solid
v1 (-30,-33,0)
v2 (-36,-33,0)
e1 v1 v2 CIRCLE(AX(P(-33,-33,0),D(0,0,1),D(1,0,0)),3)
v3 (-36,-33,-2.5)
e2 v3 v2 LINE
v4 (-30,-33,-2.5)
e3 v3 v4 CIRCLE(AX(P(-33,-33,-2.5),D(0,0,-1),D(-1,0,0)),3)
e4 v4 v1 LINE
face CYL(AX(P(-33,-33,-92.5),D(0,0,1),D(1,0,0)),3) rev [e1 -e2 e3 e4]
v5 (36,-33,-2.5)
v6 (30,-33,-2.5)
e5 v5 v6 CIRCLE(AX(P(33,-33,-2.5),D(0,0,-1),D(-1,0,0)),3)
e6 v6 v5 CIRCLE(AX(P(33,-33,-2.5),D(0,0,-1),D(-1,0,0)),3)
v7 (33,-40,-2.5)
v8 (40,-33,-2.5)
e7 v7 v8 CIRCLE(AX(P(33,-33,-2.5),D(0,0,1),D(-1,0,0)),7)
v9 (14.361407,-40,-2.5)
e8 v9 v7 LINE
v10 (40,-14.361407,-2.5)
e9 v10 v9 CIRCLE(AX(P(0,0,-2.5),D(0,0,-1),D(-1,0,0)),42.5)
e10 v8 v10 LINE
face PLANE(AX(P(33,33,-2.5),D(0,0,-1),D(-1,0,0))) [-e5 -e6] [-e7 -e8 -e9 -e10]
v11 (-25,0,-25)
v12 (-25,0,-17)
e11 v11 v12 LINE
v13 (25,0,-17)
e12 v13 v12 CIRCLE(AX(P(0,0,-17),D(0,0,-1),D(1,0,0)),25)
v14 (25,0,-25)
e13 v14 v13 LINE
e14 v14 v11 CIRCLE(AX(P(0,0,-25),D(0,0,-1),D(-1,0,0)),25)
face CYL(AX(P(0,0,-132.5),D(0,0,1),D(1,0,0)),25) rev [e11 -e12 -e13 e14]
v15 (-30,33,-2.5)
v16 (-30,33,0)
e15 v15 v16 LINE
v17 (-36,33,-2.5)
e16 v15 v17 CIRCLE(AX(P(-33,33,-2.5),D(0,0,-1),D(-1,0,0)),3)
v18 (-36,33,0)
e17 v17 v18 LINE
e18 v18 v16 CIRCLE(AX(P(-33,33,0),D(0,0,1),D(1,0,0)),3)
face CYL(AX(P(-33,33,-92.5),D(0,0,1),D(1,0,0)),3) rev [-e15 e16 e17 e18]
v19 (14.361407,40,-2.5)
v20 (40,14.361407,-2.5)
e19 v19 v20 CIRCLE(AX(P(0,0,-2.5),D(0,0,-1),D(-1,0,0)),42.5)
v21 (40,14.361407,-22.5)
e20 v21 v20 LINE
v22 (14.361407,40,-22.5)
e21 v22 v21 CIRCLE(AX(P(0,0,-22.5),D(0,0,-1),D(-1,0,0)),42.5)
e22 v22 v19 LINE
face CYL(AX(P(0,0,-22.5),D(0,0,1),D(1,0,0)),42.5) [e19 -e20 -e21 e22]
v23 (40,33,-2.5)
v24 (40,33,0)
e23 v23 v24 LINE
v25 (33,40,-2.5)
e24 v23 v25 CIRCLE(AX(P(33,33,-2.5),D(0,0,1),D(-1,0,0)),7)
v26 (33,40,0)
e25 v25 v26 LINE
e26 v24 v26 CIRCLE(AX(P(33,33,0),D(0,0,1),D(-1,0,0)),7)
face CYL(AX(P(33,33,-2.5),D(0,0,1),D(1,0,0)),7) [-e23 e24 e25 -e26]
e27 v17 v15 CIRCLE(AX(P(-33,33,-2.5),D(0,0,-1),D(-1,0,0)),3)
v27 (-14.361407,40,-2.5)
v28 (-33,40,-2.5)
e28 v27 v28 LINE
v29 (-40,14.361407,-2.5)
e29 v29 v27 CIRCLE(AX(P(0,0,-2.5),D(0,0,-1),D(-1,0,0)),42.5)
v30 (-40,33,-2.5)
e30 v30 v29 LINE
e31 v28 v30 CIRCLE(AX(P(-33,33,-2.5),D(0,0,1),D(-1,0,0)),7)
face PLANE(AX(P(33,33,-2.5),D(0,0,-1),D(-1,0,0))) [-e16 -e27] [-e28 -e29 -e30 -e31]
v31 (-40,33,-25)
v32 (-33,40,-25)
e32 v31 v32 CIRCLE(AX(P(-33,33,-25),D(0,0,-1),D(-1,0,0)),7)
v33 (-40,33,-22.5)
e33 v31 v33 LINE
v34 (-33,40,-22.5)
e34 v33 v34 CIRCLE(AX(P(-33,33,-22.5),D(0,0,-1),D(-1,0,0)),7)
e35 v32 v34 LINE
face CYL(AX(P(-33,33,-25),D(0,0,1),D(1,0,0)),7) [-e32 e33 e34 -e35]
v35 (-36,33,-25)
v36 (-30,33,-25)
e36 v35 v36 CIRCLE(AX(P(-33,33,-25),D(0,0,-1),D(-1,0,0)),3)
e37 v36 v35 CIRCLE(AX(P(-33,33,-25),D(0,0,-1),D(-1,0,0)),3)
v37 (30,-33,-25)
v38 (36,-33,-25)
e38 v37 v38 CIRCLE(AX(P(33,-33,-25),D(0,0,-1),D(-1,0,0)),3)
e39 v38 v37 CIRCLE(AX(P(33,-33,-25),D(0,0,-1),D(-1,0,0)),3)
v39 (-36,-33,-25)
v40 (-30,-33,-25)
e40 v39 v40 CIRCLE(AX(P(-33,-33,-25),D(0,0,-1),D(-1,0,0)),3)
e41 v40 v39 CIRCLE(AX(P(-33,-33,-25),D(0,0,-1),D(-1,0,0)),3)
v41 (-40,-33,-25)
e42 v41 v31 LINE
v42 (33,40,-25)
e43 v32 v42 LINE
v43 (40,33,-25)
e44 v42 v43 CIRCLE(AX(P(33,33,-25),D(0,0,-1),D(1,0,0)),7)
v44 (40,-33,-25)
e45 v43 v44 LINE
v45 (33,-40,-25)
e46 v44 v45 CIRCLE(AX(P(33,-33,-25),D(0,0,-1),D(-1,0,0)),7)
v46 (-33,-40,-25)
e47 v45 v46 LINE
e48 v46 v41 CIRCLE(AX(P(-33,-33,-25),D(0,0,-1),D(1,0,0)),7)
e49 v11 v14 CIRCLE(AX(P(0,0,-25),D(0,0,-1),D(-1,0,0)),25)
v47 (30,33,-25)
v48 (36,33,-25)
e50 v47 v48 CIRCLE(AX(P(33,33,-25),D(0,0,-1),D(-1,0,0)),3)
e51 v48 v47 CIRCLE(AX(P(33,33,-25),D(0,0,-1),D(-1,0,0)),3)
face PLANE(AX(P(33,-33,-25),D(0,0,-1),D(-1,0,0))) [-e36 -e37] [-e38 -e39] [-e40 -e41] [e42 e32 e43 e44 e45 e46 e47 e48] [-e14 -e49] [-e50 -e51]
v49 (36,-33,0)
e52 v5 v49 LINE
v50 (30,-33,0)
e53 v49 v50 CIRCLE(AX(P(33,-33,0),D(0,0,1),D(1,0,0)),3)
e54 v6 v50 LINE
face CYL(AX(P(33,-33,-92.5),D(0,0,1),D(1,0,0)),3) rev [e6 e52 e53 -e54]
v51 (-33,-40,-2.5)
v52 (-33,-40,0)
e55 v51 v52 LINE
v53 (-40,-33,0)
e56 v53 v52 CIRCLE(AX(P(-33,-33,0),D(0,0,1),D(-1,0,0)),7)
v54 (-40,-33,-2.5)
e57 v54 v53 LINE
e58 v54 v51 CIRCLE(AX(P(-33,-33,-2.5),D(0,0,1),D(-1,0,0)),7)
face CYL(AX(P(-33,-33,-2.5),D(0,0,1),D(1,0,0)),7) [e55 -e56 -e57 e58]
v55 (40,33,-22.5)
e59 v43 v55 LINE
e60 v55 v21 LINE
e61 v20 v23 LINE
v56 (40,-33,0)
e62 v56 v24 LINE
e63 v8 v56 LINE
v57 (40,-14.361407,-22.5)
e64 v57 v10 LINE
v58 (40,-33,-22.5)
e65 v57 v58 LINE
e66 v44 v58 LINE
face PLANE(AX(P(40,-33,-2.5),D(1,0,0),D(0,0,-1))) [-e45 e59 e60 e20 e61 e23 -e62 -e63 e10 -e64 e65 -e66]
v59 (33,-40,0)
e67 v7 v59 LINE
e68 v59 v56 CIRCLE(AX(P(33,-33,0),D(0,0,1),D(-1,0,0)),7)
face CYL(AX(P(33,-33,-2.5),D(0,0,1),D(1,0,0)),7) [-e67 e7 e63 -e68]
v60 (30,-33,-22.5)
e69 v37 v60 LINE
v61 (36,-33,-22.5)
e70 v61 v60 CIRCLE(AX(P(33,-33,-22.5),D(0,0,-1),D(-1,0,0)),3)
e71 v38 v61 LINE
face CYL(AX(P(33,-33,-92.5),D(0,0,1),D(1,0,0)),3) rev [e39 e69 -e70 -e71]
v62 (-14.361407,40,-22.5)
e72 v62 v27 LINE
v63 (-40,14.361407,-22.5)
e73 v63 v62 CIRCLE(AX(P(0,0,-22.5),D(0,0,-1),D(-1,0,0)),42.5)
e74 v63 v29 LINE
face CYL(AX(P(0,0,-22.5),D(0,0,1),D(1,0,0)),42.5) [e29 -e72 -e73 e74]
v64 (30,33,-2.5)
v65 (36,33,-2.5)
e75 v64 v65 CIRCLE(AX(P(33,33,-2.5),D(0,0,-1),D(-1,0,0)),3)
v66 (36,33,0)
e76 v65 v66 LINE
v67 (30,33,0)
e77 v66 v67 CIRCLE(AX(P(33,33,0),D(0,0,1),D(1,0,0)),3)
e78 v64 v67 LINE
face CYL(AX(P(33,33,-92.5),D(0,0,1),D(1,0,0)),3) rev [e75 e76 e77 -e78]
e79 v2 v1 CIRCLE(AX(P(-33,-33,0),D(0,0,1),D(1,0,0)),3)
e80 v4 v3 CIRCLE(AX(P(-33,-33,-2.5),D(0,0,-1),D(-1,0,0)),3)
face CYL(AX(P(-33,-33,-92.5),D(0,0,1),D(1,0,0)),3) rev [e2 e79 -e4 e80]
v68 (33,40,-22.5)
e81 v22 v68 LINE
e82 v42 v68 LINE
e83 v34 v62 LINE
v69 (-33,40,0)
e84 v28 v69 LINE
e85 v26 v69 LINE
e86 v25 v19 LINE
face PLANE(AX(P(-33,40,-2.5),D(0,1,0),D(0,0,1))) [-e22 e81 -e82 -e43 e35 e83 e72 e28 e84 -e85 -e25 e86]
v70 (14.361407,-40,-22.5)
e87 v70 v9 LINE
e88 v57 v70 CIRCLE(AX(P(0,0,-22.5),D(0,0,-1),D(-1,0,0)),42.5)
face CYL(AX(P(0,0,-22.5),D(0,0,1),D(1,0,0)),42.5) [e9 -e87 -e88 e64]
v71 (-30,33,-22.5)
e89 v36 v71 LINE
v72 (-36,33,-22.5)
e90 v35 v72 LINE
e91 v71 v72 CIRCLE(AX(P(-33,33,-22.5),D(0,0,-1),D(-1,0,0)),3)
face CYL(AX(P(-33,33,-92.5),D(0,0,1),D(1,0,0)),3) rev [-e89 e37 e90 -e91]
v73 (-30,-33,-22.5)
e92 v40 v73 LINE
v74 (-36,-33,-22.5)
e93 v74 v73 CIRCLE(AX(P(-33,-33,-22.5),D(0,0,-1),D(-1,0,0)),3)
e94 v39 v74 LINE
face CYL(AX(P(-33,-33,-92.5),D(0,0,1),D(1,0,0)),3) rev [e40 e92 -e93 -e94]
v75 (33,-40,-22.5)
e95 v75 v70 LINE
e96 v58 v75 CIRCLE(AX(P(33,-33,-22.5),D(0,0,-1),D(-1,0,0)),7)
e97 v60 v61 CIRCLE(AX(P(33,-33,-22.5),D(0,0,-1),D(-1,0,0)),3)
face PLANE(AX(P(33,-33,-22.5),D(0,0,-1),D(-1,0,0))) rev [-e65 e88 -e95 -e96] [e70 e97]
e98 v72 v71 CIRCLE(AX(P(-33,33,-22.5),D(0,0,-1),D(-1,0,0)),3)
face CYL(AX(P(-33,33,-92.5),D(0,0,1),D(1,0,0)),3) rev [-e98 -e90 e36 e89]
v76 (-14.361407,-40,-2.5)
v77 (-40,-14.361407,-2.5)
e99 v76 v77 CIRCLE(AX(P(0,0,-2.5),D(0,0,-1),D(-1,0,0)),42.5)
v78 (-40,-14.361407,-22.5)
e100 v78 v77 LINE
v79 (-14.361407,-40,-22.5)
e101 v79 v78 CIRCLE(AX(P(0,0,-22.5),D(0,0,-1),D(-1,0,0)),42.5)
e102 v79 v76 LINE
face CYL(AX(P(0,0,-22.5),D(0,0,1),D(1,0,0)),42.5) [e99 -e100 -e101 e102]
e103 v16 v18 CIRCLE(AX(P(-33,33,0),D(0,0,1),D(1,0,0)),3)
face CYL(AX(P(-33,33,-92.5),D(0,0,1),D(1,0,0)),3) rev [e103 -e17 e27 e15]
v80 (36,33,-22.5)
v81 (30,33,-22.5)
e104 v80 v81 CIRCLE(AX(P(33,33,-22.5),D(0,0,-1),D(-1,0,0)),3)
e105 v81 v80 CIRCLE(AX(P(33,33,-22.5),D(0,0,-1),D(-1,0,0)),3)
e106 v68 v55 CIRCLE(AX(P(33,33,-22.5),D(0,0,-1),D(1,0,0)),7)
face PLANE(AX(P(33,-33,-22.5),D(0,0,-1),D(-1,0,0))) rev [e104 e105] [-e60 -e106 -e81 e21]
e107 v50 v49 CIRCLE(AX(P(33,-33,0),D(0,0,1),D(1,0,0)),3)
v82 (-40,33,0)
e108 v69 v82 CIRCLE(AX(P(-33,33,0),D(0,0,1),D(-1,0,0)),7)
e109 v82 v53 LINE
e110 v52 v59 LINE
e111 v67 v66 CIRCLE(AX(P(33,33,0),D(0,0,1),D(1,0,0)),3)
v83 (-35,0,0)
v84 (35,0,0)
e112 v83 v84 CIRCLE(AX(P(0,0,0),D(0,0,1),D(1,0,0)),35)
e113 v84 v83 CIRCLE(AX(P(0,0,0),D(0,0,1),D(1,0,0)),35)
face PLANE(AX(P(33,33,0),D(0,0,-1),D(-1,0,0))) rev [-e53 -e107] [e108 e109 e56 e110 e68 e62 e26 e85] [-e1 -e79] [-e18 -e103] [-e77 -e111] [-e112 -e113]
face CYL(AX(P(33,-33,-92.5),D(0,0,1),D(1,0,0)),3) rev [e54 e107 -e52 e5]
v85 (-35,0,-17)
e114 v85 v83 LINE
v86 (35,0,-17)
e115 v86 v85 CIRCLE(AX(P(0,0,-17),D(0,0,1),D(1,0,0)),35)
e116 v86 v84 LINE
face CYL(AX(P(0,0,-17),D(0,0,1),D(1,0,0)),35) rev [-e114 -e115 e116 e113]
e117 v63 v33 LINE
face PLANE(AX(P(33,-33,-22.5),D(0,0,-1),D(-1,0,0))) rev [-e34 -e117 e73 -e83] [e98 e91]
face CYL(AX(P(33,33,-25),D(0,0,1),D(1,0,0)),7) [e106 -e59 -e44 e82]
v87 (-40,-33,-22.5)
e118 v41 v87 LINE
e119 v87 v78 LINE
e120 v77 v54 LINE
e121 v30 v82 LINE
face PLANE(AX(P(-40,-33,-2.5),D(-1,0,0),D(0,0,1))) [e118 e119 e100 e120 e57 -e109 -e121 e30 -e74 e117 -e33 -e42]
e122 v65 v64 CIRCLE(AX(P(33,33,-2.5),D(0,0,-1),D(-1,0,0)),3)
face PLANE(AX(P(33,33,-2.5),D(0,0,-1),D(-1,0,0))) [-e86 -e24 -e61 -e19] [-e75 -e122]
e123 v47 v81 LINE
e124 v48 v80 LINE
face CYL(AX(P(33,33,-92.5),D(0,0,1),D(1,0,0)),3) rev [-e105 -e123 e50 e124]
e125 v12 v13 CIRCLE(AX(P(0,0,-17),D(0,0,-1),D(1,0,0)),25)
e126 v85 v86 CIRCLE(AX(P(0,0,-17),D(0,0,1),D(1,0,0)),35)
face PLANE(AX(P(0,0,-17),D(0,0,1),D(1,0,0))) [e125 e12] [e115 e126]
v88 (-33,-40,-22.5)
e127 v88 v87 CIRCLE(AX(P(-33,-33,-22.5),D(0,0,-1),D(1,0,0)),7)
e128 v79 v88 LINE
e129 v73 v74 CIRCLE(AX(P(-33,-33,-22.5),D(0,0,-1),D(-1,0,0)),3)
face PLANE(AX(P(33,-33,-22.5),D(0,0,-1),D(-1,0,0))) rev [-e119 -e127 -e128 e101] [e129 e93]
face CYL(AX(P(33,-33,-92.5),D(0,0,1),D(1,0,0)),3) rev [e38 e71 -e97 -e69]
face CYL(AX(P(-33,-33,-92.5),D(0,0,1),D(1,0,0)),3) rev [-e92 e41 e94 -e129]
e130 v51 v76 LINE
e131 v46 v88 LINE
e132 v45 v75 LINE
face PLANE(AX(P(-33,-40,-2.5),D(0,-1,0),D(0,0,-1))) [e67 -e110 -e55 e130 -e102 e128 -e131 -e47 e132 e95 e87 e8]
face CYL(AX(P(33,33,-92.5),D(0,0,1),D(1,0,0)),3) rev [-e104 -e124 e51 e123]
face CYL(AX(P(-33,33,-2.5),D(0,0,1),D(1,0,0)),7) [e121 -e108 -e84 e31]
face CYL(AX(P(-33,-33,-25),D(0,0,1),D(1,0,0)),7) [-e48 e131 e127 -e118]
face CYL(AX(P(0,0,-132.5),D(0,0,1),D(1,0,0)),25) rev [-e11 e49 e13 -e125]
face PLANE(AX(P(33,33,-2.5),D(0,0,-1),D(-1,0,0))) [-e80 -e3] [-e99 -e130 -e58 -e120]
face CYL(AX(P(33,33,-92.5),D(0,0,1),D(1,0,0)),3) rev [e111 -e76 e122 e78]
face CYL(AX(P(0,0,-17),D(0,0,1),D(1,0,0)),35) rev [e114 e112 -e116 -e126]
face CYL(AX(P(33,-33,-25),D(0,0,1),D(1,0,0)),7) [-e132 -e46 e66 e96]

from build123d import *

# Parameters (mm, degrees)
FRONT_FLANGE_80X80_DEPTH = 2.5
HOUSING_BODY_DEPTH       = 20
REAR_FLANGE_80X80_DEPTH  = 2.5
MOUNTING_HOLES_SKETCH_R  = 3
MOUNTING_HOLES_4X_DEPTH  = 92.5
THROUGH_BORE_SKETCH_50_R = 25
THROUGH_BORE_50_DEPTH    = 132.5
COUNTERBORE_SKETCH_70_R  = 35
COUNTERBORE_70_DEPTH     = 17


with BuildPart() as part:
    # Front Flange Sketch → Front Flange 80x80 (new body)
    with BuildSketch(Plane.XY):
        with BuildLine():
            Line((-33, -40), (33, -40))
            ThreePointArc((33, -40), (37.949747468, -37.949747468), (40, -33))
            Line((40, -33), (40, 33))
            ThreePointArc((40, 33), (37.949747468, 37.949747468), (33, 40))
            Line((33, 40), (-33, 40))
            ThreePointArc((-33, 40), (-37.949747468, 37.949747468), (-40, 33))
            Line((-40, 33), (-40, -33))
            ThreePointArc((-40, -33), (-37.949747468, -37.949747468), (-33, -40))
        make_face()
    extrude(amount=-FRONT_FLANGE_80X80_DEPTH)

    # Housing Body Sketch → Housing Body (add)
    with BuildSketch(Plane(origin=(0, 0, -2.5), x_dir=(-1, 0, 0), z_dir=(0, 0, -1))):
        with BuildLine():
            Line((-14.361406616, 40), (14.361406616, 40))
            ThreePointArc((14.361406616, 40), (30.0520382, 30.0520382), (40, 14.361406616))
            Line((40, 14.361406616), (40, -14.361406616))
            ThreePointArc((40, -14.361406616), (30.0520382, -30.0520382), (14.361406616, -40))
            Line((14.361406616, -40), (-14.361406616, -40))
            ThreePointArc((-14.361406616, -40), (-30.0520382, -30.0520382), (-40, -14.361406616))
            Line((-40, -14.361406616), (-40, 14.361406616))
            ThreePointArc((-40, 14.361406616), (-30.0520382, 30.0520382), (-14.361406616, 40))
        make_face()
    extrude(amount=HOUSING_BODY_DEPTH)

    # Rear Flange Sketch → Rear Flange 80x80 (add)
    with BuildSketch(Plane(origin=(0, 0, -22.5), x_dir=(-1, 0, 0), z_dir=(0, 0, -1))):
        with BuildLine():
            Line((33, -40), (-33, -40))
            ThreePointArc((-33, -40), (-37.949747468, -37.949747468), (-40, -33))
            Line((-40, -33), (-40, 33))
            ThreePointArc((-40, 33), (-37.949747468, 37.949747468), (-33, 40))
            Line((-33, 40), (33, 40))
            ThreePointArc((33, 40), (37.949747468, 37.949747468), (40, 33))
            Line((40, 33), (40, -33))
            ThreePointArc((40, -33), (37.949747468, -37.949747468), (33, -40))
        make_face()
    extrude(amount=REAR_FLANGE_80X80_DEPTH)

    # Mounting Holes Sketch → Mounting Holes 4x (cut)
    with BuildSketch(Plane.XY):
        with Locations(Location((-33, 33, 0), (0, 0, 180))):
            Circle(MOUNTING_HOLES_SKETCH_R)
        with Locations(Location((33, 33, 0), (0, 0, 180))):
            Circle(MOUNTING_HOLES_SKETCH_R)
        with Locations(Location((33, -33, 0), (0, 0, 180))):
            Circle(MOUNTING_HOLES_SKETCH_R)
        with Locations(Location((-33, -33, 0), (0, 0, 180))):
            Circle(MOUNTING_HOLES_SKETCH_R)
    extrude(amount=-MOUNTING_HOLES_4X_DEPTH, mode=Mode.SUBTRACT)

    # Through Bore Sketch Ø50 → Through Bore Ø50 (cut)
    with BuildSketch(Plane.XY):
        Circle(THROUGH_BORE_SKETCH_50_R)
    extrude(amount=-THROUGH_BORE_50_DEPTH, mode=Mode.SUBTRACT)

    # Counterbore Sketch Ø70 → Counterbore Ø70 (cut)
    with BuildSketch(Plane.XY):
        Circle(COUNTERBORE_SKETCH_70_R)
    extrude(amount=-COUNTERBORE_70_DEPTH, mode=Mode.SUBTRACT)


solid = part.part
